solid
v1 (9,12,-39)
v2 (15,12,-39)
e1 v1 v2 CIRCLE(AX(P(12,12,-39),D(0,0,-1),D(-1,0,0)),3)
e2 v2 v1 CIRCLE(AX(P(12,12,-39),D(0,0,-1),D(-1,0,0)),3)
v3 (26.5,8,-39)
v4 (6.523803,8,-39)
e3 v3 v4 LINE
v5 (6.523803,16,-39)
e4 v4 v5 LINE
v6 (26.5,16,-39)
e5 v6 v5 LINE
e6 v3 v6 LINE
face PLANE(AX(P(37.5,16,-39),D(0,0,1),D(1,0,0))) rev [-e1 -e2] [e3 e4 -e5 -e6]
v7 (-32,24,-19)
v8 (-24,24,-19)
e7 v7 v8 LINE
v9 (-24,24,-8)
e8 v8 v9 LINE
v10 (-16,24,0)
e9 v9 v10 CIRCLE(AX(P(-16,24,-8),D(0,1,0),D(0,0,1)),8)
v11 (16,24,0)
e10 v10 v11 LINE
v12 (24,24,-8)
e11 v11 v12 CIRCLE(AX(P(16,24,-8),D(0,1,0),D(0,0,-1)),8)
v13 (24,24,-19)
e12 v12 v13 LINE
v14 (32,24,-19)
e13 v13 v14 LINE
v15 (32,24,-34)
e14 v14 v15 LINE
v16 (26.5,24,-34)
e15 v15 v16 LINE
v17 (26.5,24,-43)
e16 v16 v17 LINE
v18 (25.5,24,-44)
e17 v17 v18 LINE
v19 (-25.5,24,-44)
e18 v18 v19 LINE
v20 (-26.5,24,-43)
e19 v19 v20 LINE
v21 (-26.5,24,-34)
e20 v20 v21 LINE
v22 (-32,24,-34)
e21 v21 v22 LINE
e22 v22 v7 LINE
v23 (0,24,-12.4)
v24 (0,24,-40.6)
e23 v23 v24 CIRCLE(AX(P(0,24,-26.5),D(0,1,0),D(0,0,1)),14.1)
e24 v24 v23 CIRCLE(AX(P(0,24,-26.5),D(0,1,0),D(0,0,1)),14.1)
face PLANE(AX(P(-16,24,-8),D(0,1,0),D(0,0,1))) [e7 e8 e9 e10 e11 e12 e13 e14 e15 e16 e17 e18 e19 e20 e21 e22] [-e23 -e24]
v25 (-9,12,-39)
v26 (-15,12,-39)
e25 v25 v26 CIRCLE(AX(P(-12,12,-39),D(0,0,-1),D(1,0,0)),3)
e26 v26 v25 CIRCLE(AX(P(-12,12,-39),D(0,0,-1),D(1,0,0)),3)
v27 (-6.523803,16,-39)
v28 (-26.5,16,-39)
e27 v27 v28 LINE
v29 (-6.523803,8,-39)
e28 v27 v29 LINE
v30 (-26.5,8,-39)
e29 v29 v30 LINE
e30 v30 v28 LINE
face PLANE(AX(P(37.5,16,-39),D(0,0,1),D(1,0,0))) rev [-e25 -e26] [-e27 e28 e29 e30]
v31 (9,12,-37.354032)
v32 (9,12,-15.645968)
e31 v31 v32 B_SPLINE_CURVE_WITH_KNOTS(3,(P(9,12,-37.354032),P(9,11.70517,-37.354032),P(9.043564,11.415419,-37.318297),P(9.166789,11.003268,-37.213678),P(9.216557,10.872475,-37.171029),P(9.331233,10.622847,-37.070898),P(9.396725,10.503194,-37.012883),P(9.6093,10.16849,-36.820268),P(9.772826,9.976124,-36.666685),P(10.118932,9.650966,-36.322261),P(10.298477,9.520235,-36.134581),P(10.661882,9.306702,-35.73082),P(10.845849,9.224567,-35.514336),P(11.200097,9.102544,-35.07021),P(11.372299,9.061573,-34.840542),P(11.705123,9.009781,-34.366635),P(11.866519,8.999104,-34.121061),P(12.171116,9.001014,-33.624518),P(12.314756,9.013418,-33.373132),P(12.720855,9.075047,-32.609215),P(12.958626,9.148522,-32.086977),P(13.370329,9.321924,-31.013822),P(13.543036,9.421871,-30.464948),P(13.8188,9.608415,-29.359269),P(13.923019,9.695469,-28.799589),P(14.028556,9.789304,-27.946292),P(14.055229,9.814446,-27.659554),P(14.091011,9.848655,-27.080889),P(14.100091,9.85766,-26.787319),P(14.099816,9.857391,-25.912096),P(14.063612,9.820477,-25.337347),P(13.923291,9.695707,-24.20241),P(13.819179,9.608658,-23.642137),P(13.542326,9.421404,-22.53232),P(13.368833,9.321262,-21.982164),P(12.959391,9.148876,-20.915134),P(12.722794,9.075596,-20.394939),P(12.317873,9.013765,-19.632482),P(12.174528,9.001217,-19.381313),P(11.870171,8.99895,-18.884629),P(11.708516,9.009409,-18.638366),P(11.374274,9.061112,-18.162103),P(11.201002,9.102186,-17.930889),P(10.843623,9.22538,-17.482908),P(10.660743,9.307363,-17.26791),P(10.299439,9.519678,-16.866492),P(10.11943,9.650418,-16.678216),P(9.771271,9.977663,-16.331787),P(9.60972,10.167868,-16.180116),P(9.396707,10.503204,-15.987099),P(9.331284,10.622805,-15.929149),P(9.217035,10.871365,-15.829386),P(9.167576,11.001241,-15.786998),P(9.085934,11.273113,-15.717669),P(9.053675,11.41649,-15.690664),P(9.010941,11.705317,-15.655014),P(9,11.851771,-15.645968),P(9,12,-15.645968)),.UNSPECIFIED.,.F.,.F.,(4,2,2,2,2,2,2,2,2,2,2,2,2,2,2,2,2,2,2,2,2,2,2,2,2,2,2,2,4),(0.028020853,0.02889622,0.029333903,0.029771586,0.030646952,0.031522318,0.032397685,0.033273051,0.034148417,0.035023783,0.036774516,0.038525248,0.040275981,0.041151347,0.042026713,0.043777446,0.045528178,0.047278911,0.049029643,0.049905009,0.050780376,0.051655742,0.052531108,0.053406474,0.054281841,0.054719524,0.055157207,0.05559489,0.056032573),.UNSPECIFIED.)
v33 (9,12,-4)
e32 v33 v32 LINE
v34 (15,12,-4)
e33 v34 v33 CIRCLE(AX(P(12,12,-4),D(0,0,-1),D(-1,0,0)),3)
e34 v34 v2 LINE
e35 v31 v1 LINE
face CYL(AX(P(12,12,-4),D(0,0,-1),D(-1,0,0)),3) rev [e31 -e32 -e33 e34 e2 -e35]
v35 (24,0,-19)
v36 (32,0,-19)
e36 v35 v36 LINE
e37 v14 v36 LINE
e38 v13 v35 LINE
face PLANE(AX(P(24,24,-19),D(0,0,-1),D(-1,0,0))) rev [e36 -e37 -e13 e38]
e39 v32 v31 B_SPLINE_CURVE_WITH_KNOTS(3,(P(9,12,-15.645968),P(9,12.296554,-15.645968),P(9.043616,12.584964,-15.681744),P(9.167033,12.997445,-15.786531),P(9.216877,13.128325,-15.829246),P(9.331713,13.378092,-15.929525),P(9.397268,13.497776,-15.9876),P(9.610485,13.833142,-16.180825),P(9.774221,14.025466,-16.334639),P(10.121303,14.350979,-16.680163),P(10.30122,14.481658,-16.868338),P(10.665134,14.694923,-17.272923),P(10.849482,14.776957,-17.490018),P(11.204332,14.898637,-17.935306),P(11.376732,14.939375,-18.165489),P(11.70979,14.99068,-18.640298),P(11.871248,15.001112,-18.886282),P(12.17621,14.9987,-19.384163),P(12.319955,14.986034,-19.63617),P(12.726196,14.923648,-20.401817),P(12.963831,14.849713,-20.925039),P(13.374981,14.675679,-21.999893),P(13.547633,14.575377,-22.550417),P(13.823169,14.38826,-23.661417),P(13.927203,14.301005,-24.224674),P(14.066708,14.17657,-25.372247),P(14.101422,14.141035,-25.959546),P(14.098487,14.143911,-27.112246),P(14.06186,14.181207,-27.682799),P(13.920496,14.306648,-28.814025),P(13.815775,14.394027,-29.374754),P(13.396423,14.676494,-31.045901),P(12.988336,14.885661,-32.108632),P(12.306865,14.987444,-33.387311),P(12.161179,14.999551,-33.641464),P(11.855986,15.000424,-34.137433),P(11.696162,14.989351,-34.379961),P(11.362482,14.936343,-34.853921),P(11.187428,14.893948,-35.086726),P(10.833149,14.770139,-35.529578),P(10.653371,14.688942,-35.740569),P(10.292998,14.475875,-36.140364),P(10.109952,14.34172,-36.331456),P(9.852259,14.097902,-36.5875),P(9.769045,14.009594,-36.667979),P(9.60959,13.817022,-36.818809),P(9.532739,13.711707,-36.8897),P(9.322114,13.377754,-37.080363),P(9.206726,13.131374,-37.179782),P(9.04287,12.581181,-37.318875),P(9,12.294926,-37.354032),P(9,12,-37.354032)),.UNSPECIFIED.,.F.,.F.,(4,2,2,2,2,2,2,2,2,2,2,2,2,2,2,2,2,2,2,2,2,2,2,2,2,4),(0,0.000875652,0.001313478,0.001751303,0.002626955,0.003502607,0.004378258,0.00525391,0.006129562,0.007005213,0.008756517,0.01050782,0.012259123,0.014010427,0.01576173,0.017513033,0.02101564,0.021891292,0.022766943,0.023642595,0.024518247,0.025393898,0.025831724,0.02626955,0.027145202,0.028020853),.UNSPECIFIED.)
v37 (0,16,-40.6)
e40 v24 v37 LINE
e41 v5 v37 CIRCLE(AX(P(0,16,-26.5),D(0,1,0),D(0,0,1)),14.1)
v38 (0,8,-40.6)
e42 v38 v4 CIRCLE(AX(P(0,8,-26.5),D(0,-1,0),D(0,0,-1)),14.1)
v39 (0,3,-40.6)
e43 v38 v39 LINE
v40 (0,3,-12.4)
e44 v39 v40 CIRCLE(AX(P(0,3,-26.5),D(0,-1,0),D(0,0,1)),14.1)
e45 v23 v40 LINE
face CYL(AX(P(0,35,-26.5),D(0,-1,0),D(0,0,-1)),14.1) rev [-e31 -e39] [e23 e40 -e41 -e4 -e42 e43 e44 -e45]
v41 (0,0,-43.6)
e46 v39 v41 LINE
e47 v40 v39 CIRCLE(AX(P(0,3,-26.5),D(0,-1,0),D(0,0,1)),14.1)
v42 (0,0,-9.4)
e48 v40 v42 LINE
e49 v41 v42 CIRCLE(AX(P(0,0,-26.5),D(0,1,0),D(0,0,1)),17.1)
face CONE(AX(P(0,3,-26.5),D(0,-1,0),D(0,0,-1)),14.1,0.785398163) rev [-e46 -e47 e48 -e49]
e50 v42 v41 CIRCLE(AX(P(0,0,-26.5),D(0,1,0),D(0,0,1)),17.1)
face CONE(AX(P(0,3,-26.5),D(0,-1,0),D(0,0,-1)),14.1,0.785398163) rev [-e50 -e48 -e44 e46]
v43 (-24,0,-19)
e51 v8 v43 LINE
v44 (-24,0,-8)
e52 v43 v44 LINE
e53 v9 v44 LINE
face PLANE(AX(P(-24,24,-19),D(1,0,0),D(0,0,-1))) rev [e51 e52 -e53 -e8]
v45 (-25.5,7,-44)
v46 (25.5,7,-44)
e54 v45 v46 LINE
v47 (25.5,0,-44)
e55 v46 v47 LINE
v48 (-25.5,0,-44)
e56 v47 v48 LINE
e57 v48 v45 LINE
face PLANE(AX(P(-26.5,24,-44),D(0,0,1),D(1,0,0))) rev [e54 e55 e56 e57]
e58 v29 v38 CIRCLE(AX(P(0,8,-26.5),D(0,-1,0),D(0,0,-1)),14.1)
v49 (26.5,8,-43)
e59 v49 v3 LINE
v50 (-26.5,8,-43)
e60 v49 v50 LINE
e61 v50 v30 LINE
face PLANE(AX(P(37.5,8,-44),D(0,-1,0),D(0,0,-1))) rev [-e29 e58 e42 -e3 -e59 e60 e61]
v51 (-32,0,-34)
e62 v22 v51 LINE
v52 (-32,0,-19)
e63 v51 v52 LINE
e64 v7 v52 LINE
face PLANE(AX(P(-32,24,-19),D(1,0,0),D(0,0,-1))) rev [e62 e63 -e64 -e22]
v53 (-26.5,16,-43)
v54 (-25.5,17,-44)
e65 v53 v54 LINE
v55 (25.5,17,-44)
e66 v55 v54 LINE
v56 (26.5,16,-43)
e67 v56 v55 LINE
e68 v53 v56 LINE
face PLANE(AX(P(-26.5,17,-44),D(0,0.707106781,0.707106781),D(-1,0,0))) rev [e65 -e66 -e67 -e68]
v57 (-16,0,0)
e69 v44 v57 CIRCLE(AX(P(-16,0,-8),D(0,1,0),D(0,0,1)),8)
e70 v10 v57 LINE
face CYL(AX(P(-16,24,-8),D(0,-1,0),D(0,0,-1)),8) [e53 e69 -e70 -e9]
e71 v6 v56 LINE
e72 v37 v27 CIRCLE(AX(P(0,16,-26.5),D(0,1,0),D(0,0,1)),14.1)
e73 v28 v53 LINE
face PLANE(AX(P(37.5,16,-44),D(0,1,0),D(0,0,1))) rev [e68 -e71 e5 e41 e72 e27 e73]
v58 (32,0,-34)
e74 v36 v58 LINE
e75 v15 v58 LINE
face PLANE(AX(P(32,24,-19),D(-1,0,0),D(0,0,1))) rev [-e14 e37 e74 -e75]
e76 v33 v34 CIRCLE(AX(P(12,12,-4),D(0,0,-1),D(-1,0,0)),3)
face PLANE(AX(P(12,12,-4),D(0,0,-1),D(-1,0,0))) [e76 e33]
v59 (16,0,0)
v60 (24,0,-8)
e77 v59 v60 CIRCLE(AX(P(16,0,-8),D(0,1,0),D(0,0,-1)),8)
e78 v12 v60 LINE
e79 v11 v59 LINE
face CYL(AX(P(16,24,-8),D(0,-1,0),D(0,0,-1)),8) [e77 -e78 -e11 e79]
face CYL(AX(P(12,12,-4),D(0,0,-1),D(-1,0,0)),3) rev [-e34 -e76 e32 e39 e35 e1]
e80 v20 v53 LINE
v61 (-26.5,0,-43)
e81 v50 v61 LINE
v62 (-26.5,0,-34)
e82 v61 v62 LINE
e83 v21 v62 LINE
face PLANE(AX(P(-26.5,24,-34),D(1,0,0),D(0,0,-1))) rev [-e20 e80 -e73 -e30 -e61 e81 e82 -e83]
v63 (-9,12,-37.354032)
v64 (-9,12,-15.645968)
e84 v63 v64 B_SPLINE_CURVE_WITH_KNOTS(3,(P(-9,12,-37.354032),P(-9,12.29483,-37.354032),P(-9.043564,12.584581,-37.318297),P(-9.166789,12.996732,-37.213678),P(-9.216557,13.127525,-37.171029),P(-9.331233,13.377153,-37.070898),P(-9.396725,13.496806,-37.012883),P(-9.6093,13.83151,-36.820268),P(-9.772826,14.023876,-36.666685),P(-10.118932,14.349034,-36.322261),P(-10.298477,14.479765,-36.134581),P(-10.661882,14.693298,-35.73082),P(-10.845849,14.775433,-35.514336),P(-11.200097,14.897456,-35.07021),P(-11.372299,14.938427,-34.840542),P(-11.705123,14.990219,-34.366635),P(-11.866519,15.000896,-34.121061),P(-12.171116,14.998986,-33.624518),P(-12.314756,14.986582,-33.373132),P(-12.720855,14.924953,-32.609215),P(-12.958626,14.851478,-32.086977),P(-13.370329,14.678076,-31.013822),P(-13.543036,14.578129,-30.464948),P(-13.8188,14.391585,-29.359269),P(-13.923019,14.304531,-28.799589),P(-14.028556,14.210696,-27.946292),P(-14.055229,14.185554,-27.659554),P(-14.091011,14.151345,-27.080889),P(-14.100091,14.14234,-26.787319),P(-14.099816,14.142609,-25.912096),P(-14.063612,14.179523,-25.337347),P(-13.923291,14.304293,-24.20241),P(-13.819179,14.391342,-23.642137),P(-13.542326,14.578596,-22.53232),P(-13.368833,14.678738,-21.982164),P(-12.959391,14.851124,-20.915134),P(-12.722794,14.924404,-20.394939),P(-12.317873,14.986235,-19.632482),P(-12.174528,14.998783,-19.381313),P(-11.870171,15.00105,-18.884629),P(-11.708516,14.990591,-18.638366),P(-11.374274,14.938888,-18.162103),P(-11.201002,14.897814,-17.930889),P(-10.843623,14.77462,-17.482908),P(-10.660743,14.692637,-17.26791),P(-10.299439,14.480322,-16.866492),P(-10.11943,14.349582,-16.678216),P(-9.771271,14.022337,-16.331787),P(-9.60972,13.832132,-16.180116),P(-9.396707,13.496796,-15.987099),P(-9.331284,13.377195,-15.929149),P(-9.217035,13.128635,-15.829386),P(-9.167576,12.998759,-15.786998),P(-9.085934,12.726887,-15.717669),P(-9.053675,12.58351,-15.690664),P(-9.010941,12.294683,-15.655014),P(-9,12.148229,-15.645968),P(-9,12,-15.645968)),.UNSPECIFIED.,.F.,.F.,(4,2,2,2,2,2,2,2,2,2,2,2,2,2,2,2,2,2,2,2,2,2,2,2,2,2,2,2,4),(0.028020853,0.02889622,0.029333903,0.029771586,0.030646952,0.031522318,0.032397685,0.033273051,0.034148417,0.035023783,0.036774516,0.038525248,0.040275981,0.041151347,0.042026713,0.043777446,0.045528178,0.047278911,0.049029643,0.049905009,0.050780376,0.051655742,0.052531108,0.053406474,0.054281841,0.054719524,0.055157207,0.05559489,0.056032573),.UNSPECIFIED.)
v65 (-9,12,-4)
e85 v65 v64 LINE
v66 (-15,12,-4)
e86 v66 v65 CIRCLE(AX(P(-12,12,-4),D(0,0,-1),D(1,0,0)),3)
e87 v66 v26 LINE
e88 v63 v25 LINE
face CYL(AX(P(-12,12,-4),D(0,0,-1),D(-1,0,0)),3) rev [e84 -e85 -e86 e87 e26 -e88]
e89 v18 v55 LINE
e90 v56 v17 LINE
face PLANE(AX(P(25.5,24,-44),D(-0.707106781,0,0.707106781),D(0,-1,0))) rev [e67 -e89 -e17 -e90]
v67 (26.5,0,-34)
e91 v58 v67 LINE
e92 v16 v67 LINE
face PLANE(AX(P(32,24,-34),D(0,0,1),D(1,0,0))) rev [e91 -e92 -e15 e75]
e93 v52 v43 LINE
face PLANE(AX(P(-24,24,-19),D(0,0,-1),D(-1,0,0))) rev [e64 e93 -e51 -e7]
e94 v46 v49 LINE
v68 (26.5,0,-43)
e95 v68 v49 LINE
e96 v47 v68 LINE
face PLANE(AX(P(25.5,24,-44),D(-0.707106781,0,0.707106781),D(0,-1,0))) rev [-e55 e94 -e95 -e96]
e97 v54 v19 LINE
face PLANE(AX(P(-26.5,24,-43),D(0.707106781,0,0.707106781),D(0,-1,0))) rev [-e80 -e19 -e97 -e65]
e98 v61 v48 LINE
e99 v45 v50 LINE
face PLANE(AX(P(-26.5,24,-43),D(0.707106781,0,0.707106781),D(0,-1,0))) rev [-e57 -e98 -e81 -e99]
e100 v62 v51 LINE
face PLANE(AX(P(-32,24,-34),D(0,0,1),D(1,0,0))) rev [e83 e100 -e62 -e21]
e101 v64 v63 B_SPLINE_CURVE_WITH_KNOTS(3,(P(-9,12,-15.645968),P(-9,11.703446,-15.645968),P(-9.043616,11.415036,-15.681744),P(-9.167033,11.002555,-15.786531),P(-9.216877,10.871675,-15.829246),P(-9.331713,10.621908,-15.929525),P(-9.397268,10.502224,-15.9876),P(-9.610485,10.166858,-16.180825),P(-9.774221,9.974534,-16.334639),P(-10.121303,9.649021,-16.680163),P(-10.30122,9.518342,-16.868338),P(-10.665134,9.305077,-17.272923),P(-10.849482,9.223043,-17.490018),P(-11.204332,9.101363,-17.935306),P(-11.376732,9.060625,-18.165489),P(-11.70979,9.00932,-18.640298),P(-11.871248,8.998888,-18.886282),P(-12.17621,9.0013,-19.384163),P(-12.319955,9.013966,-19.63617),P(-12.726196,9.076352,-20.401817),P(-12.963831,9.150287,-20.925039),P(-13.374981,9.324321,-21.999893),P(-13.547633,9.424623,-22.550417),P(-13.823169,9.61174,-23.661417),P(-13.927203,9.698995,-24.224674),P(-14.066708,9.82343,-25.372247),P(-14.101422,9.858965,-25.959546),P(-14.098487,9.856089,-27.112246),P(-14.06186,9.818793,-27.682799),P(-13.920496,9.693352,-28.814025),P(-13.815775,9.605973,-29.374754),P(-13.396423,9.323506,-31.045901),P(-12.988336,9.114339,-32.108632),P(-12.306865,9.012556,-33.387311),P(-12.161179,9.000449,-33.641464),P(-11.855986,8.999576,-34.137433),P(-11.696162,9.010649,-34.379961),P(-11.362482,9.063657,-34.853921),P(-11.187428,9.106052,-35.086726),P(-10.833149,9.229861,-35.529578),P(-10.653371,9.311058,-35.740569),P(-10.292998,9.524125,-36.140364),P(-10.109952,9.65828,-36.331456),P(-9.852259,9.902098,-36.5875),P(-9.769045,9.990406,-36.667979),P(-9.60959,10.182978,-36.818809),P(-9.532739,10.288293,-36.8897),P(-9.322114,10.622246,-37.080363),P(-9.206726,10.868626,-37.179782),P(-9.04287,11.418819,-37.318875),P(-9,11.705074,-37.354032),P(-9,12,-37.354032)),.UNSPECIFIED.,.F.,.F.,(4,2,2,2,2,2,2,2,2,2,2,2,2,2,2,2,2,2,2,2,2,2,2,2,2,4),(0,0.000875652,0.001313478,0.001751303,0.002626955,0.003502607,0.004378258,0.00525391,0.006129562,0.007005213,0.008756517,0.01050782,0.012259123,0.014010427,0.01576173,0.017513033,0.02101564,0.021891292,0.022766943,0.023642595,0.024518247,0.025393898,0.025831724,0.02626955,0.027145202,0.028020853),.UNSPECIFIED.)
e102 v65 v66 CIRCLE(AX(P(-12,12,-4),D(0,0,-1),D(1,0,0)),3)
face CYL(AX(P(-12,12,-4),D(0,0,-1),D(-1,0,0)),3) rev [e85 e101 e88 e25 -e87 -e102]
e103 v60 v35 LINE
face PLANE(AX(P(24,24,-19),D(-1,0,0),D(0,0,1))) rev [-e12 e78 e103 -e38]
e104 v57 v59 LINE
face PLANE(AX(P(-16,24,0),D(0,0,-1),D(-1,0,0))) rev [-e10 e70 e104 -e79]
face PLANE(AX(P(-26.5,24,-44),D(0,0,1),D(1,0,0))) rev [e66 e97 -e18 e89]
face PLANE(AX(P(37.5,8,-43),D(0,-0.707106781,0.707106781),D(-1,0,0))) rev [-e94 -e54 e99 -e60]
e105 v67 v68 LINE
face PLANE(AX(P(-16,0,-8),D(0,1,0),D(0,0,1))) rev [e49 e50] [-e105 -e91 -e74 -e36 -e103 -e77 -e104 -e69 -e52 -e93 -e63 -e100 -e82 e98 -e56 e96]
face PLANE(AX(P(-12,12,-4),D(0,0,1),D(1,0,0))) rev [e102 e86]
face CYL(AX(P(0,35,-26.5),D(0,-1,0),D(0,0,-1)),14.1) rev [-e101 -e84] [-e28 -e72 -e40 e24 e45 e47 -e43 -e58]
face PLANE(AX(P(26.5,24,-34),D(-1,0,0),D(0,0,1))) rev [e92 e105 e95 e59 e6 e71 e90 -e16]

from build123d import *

# Parameters (mm, degrees)
BOSS_EXTRUDE1_DEPTH = 24
SKETCH2_W           = 5
SKETCH2_H           = 8
CUT_EXTRUDE1_DEPTH  = 64
SKETCH3_R           = 3
CUT_EXTRUDE2_DEPTH  = 35
SKETCH4_R           = 14.1
CUT_EXTRUDE3_DEPTH  = 35
CHAMFER1_SIZE       = 1
CHAMFER2_SIZE       = 3


with BuildPart() as part:
    # Sketch1 → Boss-Extrude1 (new body)
    with BuildSketch(Plane(origin=(0, 0, 0), x_dir=(1, 0, 0), z_dir=(0, 1, 0))):
        with BuildLine():
            Line((-24, 19), (-24, 8))
            ThreePointArc((-24, 8), (-21.656854249, 2.343145751), (-16, 0))
            Line((-16, 0), (16, 0))
            ThreePointArc((16, 0), (21.656854249, 2.343145751), (24, 8))
            Line((24, 8), (24, 19))
            Line((24, 19), (32, 19))
            Line((32, 19), (32, 34))
            Line((32, 34), (26.5, 34))
            Line((26.5, 34), (26.5, 44))
            Line((26.5, 44), (-26.5, 44))
            Line((-26.5, 44), (-26.5, 34))
            Line((-26.5, 34), (-32, 34))
            Line((-32, 34), (-32, 19))
            Line((-32, 19), (-24, 19))
        make_face()
    extrude(amount=BOSS_EXTRUDE1_DEPTH)

    # Sketch2 → Cut-Extrude1 (cut)
    with BuildSketch(Plane.ZY.offset(26.5)):
        with Locations((-41.5, 12)):
            Rectangle(SKETCH2_W, SKETCH2_H)
    extrude(amount=-CUT_EXTRUDE1_DEPTH, mode=Mode.SUBTRACT)

    # Sketch3 → Cut-Extrude2 (cut)
    with BuildSketch(Plane(origin=(0, 0, -39), x_dir=(-1, 0, 0), z_dir=(0, 0, -1))):
        with Locations((-12, 12)):
            Circle(SKETCH3_R)
        with Locations(Location((12, 12, 0), (0, 0, 180))):
            Circle(SKETCH3_R)
    extrude(amount=-CUT_EXTRUDE2_DEPTH, mode=Mode.SUBTRACT)

    # Sketch4 → Cut-Extrude3 (cut)
    with BuildSketch(Plane.XZ):
        with Locations(Location((0, -26.5, 0), (0, 0, 270))):
            Circle(SKETCH4_R)
    extrude(amount=-CUT_EXTRUDE3_DEPTH, mode=Mode.SUBTRACT)

    # Chamfer1
    chamfer1_edges = [part.edges().sort_by_distance(p)[0] for p in [
        (-26.5, 20, -44),
        (26.5, 20, -44),
        (-26.5, 4, -44),
        (26.5, 4, -44),
        (0, 8, -44),
        (0, 16, -44),
    ]]
    chamfer(chamfer1_edges, length=CHAMFER1_SIZE)

    # Chamfer2
    chamfer2_edges = [part.edges().sort_by_distance(p)[0] for p in [
        (0, 0, -12.4),
    ]]
    chamfer(chamfer2_edges, length=CHAMFER2_SIZE)


solid = part.part
